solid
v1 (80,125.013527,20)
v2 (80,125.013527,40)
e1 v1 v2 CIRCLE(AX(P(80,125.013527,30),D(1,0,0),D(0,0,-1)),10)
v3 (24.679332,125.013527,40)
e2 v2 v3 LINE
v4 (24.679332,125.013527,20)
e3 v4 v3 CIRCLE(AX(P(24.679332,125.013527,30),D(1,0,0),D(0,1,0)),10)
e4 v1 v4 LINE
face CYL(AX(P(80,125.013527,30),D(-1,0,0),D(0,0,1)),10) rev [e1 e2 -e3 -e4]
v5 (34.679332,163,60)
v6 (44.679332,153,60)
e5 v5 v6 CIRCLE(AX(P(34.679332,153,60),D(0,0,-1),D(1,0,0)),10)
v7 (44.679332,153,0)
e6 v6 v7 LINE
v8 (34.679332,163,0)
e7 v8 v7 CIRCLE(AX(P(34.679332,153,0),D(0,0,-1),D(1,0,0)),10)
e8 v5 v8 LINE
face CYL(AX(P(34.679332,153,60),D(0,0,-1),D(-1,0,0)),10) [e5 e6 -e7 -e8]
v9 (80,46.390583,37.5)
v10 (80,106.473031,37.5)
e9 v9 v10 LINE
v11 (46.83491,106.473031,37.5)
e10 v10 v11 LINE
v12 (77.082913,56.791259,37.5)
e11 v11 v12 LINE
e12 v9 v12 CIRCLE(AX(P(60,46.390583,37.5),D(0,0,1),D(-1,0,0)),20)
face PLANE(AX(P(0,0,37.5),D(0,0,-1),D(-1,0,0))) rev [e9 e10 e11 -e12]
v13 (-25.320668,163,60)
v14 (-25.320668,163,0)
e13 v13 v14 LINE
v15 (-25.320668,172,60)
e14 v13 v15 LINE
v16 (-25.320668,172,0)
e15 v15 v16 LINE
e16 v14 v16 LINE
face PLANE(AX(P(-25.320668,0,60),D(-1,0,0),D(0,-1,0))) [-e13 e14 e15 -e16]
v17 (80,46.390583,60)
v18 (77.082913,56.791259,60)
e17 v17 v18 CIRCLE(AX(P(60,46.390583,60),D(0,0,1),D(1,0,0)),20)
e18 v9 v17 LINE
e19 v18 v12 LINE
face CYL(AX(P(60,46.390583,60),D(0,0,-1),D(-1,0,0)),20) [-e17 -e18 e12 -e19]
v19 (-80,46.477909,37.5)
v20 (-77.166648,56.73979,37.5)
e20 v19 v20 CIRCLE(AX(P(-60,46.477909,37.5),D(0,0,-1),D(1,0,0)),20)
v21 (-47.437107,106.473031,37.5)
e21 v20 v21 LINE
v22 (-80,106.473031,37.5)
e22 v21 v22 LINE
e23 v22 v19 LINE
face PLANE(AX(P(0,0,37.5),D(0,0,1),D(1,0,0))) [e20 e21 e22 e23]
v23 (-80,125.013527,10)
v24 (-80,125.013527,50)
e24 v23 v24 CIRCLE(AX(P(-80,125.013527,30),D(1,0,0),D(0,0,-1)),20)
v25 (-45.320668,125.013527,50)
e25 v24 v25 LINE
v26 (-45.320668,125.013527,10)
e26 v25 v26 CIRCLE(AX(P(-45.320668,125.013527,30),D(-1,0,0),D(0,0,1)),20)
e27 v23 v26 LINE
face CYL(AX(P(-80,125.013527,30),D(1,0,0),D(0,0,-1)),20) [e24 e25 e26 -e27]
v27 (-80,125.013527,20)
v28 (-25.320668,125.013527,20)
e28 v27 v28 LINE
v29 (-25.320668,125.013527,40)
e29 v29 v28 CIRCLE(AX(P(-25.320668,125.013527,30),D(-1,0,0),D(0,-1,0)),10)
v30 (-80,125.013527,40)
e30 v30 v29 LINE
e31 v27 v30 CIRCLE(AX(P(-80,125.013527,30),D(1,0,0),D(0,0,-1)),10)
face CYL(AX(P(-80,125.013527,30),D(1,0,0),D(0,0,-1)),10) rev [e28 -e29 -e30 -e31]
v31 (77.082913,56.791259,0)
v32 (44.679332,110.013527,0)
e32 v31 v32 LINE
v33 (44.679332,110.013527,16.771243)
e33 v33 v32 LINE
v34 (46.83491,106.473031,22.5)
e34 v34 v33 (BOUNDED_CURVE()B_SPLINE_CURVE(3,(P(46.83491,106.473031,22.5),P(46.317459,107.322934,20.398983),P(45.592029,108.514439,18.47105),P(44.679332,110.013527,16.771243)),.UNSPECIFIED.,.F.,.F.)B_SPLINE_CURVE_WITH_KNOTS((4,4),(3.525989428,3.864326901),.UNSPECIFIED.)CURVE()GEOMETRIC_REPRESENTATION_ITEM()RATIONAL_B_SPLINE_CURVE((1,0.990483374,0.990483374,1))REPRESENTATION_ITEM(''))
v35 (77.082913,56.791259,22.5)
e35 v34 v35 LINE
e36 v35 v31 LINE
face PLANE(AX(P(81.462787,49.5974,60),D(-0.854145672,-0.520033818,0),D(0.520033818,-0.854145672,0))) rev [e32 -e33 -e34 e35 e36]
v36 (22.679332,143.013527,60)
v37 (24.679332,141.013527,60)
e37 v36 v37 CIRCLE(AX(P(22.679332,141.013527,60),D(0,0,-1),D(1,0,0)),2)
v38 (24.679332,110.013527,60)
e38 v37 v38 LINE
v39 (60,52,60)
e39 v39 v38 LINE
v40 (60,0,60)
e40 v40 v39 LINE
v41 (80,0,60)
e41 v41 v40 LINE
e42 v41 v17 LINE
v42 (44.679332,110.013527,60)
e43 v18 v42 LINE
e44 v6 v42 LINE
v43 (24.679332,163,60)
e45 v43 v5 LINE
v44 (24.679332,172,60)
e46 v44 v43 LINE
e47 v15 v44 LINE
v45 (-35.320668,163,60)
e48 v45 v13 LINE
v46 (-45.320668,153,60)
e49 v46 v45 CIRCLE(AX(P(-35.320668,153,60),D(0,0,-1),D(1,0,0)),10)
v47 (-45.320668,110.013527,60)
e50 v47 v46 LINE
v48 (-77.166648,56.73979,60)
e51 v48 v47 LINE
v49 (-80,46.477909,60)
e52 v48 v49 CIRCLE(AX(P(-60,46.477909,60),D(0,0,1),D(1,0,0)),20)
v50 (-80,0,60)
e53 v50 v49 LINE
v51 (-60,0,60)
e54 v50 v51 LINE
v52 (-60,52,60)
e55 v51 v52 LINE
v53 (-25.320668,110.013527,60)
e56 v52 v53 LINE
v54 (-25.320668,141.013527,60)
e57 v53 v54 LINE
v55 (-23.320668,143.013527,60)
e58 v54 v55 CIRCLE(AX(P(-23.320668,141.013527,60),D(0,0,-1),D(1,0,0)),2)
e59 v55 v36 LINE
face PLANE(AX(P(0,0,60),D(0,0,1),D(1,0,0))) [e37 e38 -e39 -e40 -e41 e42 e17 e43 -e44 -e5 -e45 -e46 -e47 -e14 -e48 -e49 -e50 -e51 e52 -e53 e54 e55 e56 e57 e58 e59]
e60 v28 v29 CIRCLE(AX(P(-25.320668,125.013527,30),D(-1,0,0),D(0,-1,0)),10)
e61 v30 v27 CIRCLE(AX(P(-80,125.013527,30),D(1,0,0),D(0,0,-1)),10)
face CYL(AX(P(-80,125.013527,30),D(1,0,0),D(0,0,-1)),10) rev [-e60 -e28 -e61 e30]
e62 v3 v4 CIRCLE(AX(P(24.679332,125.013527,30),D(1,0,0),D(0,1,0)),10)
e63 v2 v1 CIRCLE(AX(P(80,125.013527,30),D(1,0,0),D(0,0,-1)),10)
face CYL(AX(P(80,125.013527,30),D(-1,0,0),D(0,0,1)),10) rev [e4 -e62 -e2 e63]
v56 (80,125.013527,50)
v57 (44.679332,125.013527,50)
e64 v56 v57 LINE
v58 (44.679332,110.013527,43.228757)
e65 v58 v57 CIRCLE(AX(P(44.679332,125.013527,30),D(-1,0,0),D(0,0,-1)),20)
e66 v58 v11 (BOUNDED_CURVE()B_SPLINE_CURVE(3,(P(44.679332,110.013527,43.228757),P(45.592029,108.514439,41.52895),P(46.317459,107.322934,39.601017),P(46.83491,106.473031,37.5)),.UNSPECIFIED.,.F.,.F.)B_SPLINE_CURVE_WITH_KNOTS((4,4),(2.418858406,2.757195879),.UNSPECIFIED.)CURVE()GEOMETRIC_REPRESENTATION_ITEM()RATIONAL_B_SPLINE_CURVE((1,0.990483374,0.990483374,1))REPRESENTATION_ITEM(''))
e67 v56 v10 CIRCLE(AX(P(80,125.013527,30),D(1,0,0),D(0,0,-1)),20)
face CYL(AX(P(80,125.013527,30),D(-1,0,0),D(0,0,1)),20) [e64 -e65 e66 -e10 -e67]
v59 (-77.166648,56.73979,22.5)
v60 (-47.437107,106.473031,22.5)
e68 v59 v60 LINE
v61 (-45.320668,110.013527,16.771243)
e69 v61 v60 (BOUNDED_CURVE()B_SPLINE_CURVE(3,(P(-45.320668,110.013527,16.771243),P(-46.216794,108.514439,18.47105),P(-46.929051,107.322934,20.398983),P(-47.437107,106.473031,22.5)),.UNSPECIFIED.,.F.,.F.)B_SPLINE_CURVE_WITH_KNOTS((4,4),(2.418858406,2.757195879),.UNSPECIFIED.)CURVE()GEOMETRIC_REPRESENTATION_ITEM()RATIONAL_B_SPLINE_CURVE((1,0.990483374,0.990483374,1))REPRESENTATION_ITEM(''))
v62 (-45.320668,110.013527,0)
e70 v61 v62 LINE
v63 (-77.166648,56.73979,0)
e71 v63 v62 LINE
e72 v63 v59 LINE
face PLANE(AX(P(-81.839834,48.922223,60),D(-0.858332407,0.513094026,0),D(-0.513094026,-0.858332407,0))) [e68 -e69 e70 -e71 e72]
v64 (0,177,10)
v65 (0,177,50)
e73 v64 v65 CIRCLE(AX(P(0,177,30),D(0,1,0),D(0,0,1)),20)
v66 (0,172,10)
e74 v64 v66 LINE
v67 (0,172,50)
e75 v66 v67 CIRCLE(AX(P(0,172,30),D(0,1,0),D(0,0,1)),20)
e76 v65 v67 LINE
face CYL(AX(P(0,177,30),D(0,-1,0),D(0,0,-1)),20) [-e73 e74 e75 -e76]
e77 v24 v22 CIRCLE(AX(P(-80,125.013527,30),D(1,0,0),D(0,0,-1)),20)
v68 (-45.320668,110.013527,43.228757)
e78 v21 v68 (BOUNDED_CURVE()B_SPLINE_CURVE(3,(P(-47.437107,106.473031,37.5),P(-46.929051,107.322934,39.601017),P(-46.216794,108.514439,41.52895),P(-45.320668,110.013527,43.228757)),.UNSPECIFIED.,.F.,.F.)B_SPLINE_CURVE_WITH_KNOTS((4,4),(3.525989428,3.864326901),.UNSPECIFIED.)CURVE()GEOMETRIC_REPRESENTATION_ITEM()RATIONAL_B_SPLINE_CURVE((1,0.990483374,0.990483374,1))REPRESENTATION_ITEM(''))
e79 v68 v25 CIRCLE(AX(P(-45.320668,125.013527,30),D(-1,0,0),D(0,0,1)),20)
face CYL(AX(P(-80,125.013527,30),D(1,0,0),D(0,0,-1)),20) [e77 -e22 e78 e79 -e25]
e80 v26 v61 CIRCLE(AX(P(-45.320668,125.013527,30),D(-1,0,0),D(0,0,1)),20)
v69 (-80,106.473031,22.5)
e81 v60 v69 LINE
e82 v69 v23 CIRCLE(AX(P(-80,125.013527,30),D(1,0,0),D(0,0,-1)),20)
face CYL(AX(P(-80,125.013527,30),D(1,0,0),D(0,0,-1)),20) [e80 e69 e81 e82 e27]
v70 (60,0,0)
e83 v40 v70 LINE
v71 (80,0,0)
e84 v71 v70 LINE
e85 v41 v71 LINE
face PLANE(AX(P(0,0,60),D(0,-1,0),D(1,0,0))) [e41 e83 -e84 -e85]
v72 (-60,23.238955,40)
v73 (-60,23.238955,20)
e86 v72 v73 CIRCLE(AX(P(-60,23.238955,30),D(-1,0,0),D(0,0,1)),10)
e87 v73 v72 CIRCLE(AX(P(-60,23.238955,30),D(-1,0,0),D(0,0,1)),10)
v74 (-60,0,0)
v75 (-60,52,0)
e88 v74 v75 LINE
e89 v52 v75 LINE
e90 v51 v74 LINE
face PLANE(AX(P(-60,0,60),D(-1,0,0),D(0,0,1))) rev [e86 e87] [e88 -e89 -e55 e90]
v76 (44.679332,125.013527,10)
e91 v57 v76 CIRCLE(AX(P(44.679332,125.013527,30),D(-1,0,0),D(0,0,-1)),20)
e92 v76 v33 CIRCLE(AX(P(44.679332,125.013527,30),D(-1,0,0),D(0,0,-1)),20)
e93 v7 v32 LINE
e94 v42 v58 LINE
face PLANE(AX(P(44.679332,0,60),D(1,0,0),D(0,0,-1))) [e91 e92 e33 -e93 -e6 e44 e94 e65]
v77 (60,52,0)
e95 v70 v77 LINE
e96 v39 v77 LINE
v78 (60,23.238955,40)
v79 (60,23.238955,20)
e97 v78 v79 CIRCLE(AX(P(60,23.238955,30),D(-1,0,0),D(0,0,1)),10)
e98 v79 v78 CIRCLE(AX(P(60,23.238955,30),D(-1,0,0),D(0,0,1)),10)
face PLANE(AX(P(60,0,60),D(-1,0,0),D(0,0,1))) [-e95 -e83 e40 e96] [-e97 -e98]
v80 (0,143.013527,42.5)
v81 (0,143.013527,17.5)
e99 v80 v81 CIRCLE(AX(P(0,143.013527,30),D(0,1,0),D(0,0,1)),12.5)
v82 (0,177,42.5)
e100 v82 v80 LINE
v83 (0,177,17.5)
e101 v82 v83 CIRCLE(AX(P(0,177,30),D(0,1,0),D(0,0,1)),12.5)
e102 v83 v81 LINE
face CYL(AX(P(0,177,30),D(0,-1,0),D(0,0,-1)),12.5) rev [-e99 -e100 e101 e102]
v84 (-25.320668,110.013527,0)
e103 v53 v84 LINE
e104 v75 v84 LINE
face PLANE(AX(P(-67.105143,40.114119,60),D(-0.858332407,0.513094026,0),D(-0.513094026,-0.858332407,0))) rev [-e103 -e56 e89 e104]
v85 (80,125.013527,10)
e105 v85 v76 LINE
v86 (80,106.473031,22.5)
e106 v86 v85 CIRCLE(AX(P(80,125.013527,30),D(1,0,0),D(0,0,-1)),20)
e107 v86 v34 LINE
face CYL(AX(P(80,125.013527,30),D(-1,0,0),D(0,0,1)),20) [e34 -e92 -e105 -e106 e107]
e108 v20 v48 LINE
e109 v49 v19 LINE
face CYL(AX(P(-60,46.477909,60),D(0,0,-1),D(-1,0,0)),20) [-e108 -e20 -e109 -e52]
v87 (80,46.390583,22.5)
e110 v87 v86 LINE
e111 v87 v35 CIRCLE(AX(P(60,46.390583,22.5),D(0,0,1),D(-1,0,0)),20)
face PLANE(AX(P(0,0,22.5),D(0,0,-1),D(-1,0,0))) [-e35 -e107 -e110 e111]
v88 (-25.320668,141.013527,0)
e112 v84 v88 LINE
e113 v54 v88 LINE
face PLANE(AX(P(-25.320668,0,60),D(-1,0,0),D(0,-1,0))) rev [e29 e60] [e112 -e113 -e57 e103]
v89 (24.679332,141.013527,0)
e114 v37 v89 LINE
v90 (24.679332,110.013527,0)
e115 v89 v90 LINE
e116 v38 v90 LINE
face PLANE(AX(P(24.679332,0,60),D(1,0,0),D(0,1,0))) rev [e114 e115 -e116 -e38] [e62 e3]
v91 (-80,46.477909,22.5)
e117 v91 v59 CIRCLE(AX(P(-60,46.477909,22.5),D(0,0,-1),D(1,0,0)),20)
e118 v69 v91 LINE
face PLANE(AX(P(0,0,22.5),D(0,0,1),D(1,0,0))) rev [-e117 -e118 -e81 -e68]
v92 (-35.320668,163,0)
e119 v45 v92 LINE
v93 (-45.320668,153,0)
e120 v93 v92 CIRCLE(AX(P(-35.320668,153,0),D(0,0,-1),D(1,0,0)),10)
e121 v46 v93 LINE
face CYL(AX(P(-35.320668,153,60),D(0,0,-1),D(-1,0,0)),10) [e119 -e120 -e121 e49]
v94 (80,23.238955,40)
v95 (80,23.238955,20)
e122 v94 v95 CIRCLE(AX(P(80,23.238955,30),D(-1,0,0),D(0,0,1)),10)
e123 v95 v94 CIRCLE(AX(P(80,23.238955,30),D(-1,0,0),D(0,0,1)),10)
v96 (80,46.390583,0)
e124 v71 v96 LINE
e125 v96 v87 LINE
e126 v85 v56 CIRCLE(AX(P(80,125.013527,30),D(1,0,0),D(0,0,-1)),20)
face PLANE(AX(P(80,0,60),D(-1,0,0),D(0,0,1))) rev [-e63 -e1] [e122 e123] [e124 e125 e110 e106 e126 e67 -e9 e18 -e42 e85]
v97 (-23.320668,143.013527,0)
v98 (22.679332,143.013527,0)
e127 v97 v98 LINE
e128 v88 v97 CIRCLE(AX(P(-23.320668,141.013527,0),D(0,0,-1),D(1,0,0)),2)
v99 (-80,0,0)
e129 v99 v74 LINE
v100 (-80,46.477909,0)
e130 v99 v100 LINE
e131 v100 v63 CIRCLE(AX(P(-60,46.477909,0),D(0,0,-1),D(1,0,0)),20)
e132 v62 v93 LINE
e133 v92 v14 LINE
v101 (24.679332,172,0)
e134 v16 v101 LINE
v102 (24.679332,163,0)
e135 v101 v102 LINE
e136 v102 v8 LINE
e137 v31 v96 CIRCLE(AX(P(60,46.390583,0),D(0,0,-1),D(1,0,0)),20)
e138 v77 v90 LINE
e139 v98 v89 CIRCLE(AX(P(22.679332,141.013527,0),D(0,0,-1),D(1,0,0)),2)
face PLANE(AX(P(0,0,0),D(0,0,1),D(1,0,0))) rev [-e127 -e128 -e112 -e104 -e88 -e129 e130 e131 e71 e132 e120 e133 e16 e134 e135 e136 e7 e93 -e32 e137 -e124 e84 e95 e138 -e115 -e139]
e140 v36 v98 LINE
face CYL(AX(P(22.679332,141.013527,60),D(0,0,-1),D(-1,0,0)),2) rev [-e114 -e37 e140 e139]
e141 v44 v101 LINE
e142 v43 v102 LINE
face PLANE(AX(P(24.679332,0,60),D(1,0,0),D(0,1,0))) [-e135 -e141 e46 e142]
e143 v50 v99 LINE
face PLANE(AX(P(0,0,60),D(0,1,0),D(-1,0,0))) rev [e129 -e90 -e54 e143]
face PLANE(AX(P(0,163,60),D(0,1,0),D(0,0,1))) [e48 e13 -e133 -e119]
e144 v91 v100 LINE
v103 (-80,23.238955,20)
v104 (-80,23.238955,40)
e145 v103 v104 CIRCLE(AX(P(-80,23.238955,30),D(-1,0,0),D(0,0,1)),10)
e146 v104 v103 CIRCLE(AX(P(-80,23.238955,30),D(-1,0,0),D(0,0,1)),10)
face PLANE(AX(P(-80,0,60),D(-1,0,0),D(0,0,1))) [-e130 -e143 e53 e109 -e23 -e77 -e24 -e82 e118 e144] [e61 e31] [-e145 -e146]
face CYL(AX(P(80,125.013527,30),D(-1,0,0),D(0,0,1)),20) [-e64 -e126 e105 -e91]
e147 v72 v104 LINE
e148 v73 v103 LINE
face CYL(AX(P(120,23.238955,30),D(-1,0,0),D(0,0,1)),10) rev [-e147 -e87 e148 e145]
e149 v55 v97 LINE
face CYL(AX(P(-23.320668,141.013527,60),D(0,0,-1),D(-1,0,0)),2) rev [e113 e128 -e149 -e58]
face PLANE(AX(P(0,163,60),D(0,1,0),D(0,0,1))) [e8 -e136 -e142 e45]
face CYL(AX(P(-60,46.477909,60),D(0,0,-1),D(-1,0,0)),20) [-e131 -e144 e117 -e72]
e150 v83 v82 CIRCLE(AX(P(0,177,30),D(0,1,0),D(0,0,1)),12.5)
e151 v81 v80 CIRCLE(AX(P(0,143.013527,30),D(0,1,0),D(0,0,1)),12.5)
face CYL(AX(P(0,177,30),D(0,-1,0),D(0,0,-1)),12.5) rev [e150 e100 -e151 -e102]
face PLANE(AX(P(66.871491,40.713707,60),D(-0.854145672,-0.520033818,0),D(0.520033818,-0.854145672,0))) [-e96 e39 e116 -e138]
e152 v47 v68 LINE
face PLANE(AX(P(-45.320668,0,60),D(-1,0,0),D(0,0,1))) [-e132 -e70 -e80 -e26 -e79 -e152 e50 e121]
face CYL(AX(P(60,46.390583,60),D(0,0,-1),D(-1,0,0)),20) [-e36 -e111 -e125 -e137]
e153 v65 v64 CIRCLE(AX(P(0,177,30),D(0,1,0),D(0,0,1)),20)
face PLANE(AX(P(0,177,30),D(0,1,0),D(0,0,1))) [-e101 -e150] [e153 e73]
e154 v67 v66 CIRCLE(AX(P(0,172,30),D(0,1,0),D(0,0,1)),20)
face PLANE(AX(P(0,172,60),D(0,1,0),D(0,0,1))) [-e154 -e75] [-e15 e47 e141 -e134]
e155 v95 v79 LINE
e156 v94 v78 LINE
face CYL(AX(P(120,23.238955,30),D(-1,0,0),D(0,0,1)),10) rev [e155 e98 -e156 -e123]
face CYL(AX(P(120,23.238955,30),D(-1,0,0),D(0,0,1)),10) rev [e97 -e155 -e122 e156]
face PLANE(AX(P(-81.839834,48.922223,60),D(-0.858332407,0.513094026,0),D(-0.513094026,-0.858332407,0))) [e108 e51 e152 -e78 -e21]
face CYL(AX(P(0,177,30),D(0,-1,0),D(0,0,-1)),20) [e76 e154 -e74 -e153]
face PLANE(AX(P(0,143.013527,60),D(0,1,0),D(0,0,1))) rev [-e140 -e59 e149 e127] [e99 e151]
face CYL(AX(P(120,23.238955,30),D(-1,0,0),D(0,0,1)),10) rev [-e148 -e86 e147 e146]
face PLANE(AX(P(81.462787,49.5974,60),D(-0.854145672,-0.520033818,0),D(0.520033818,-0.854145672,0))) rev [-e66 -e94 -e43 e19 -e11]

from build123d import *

# Parameters (mm, degrees)
INVERTED_U_FORK_BODY_DEPTH    = 60
TOP_COLLAR_BOSS_SKETCH_R      = 20
TOP_COLLAR_BOSS_SKETCH_R_2    = 12.5
TOP_COLLAR_BOSS_DEPTH         = 5
COLLAR_START                  = -50
COLLAR_BORE_SKETCH_R          = 12.5
COLLAR_BORE_25_DEPTH          = 50
LEG_BLEND_FILLET_R20_A_R      = 20
LEG_BLEND_FILLET_R20_B_R      = 20
LEG_PIN_HOLE_SKETCH_R         = 10
LEG_PIN_HOLES_20_DEPTH        = 200
SIDE_BOSS_A_SKETCH_R          = 20
SIDE_BOSS_A_SKETCH_R_2        = 10
SIDE_BOSS_A_DEPTH             = 50
SIDE_START                    = -50
SIDE_BOSS_B_SKETCH_R          = 20
SIDE_BOSS_B_SKETCH_R_2        = 10
SIDE_BOSS_B_DEPTH             = 50
SIDE_START_2                  = -180
SIDE_BOSS_CROSS_BORE_SKETCH_R = 10
SIDE_BOSS_CROSS_BORE_20_DEPTH = 180
WEB_RIB_DEPTH                 = 7.5


with BuildPart() as part:
    # Fork Profile Sketch → Inverted U Fork Body (new body)
    with BuildSketch(Plane.XY):
        with BuildLine():
            Line((-25.320668346, 110.01352712), (-25.320668346, 141.01352712))
            ThreePointArc((-25.320668346, 141.01352712), (-24.734881908, 142.427740683), (-23.320668346, 143.01352712))
            Line((-23.320668346, 143.01352712), (22.679331654, 143.01352712))
            ThreePointArc((22.679331654, 143.01352712), (24.093545217, 142.427740683), (24.679331654, 141.01352712))
            Line((24.679331654, 141.01352712), (24.679331654, 110.01352712))
            Line((24.679331654, 110.01352712), (60, 52))
            Line((60, 52), (60, 0))
            Line((60, 0), (80, 0))
            Line((80, 0), (80, 52))
            Line((80, 52), (44.679331654, 110.01352712))
            Line((44.679331654, 110.01352712), (44.679331654, 153))
            ThreePointArc((44.679331654, 153), (41.750399466, 160.071067812), (34.679331654, 163))
            Line((34.679331654, 163), (24.679331654, 163))
            Line((24.679331654, 163), (24.679331654, 172))
            Line((24.679331654, 172), (10, 172))
            Line((10, 172), (-10, 172))
            Line((-10, 172), (-25.320668346, 172))
            Line((-25.320668346, 172), (-25.320668346, 163))
            Line((-25.320668346, 163), (-35.320668346, 163))
            ThreePointArc((-35.320668346, 163), (-42.391736158, 160.071067812), (-45.320668346, 153))
            Line((-45.320668346, 153), (-45.320668346, 110.01352712))
            Line((-45.320668346, 110.01352712), (-80, 52))
            Line((-80, 52), (-80, 0))
            Line((-80, 0), (-60, 0))
            Line((-60, 0), (-60, 52))
            Line((-60, 52), (-25.320668346, 110.01352712))
        make_face()
    extrude(amount=INVERTED_U_FORK_BODY_DEPTH)

    # Top Collar Boss Sketch → Top Collar Boss (add)
    with BuildSketch(Plane(origin=(0, 172, 0), x_dir=(1, 0, 0), z_dir=(0, 1, 0))):
        with Locations(Location((0, -30, 0), (0, 0, 270))):
            Circle(TOP_COLLAR_BOSS_SKETCH_R)
        with Locations(Location((0, -30, 0), (0, 0, 270))):
            Circle(TOP_COLLAR_BOSS_SKETCH_R_2, mode=Mode.SUBTRACT)
    extrude(amount=TOP_COLLAR_BOSS_DEPTH)

    # Collar Bore Sketch → Collar Bore Ø25 (cut)
    with BuildSketch(Plane(origin=(0, 172, 0), x_dir=(1, 0, 0), z_dir=(0, 1, 0)).offset(COLLAR_START)):
        with Locations(Location((0, -30, 0), (0, 0, 270))):
            Circle(COLLAR_BORE_SKETCH_R)
    extrude(amount=COLLAR_BORE_25_DEPTH, mode=Mode.SUBTRACT)

    # Leg Blend Fillet R20 A
    leg_blend_fillet_r20_a_edges = [part.edges().sort_by_distance(p)[0] for p in [
        (-80, 52, 30),
    ]]
    fillet(leg_blend_fillet_r20_a_edges, radius=LEG_BLEND_FILLET_R20_A_R)

    # Leg Blend Fillet R20 B
    leg_blend_fillet_r20_b_edges = [part.edges().sort_by_distance(p)[0] for p in [
        (80, 52, 30),
    ]]
    fillet(leg_blend_fillet_r20_b_edges, radius=LEG_BLEND_FILLET_R20_B_R)

    # Leg Pin Hole Sketch → Leg Pin Holes Ø20 (cut)
    with BuildSketch(Plane.ZY.offset(80)):
        with Locations((30, 23.238954536)):
            Circle(LEG_PIN_HOLE_SKETCH_R)
    extrude(amount=-LEG_PIN_HOLES_20_DEPTH, mode=Mode.SUBTRACT)

    # Side Boss A Sketch → Side Boss A (add)
    with BuildSketch(Plane(origin=(30, 0, 0), x_dir=(0, 0, -1), z_dir=(1, 0, 0))):
        with Locations(Location((-30, 125.01352712, 0), (0, 0, 228.590377891))):
            Circle(SIDE_BOSS_A_SKETCH_R)
        with Locations((-30, 125.01352712)):
            Circle(SIDE_BOSS_A_SKETCH_R_2, mode=Mode.SUBTRACT)
    extrude(amount=SIDE_BOSS_A_DEPTH)

    # Side Boss B Sketch → Side Boss B (add)
    with BuildSketch(Plane(origin=(-30, 0, 0), x_dir=(0, 0, -1), z_dir=(1, 0, 0)).offset(SIDE_START)):
        with Locations(Location((-30, 125.01352712, 0), (0, 0, 228.590377891))):
            Circle(SIDE_BOSS_B_SKETCH_R)
        with Locations((-30, 125.01352712)):
            Circle(SIDE_BOSS_B_SKETCH_R_2, mode=Mode.SUBTRACT)
    extrude(amount=SIDE_BOSS_B_DEPTH)

    # Side Boss Cross Bore Sketch → Side Boss Cross Bore Ø20 (cut)
    with BuildSketch(Plane(origin=(44.679331654, 0, 0), x_dir=(0, 0, -1), z_dir=(1, 0, 0)).offset(SIDE_START_2)):
        with Locations(Location((-30, 125.01352712, 0), (0, 0, 90))):
            Circle(SIDE_BOSS_CROSS_BORE_SKETCH_R)
    extrude(amount=SIDE_BOSS_CROSS_BORE_20_DEPTH, mode=Mode.SUBTRACT)

    # Web Rib Sketch → Web Rib (add, symmetric)
    with BuildSketch(Plane.XY.offset(30)):
        Polygon((-45.320668346, 110.01352712), (-80, 110.01352712), (-80, 46.477909073), align=None)
        Polygon((44.679331654, 110.01352712), (80, 110.01352712), (80, 46.390582944), align=None)
    extrude(amount=WEB_RIB_DEPTH, both=True)


solid = part.part
